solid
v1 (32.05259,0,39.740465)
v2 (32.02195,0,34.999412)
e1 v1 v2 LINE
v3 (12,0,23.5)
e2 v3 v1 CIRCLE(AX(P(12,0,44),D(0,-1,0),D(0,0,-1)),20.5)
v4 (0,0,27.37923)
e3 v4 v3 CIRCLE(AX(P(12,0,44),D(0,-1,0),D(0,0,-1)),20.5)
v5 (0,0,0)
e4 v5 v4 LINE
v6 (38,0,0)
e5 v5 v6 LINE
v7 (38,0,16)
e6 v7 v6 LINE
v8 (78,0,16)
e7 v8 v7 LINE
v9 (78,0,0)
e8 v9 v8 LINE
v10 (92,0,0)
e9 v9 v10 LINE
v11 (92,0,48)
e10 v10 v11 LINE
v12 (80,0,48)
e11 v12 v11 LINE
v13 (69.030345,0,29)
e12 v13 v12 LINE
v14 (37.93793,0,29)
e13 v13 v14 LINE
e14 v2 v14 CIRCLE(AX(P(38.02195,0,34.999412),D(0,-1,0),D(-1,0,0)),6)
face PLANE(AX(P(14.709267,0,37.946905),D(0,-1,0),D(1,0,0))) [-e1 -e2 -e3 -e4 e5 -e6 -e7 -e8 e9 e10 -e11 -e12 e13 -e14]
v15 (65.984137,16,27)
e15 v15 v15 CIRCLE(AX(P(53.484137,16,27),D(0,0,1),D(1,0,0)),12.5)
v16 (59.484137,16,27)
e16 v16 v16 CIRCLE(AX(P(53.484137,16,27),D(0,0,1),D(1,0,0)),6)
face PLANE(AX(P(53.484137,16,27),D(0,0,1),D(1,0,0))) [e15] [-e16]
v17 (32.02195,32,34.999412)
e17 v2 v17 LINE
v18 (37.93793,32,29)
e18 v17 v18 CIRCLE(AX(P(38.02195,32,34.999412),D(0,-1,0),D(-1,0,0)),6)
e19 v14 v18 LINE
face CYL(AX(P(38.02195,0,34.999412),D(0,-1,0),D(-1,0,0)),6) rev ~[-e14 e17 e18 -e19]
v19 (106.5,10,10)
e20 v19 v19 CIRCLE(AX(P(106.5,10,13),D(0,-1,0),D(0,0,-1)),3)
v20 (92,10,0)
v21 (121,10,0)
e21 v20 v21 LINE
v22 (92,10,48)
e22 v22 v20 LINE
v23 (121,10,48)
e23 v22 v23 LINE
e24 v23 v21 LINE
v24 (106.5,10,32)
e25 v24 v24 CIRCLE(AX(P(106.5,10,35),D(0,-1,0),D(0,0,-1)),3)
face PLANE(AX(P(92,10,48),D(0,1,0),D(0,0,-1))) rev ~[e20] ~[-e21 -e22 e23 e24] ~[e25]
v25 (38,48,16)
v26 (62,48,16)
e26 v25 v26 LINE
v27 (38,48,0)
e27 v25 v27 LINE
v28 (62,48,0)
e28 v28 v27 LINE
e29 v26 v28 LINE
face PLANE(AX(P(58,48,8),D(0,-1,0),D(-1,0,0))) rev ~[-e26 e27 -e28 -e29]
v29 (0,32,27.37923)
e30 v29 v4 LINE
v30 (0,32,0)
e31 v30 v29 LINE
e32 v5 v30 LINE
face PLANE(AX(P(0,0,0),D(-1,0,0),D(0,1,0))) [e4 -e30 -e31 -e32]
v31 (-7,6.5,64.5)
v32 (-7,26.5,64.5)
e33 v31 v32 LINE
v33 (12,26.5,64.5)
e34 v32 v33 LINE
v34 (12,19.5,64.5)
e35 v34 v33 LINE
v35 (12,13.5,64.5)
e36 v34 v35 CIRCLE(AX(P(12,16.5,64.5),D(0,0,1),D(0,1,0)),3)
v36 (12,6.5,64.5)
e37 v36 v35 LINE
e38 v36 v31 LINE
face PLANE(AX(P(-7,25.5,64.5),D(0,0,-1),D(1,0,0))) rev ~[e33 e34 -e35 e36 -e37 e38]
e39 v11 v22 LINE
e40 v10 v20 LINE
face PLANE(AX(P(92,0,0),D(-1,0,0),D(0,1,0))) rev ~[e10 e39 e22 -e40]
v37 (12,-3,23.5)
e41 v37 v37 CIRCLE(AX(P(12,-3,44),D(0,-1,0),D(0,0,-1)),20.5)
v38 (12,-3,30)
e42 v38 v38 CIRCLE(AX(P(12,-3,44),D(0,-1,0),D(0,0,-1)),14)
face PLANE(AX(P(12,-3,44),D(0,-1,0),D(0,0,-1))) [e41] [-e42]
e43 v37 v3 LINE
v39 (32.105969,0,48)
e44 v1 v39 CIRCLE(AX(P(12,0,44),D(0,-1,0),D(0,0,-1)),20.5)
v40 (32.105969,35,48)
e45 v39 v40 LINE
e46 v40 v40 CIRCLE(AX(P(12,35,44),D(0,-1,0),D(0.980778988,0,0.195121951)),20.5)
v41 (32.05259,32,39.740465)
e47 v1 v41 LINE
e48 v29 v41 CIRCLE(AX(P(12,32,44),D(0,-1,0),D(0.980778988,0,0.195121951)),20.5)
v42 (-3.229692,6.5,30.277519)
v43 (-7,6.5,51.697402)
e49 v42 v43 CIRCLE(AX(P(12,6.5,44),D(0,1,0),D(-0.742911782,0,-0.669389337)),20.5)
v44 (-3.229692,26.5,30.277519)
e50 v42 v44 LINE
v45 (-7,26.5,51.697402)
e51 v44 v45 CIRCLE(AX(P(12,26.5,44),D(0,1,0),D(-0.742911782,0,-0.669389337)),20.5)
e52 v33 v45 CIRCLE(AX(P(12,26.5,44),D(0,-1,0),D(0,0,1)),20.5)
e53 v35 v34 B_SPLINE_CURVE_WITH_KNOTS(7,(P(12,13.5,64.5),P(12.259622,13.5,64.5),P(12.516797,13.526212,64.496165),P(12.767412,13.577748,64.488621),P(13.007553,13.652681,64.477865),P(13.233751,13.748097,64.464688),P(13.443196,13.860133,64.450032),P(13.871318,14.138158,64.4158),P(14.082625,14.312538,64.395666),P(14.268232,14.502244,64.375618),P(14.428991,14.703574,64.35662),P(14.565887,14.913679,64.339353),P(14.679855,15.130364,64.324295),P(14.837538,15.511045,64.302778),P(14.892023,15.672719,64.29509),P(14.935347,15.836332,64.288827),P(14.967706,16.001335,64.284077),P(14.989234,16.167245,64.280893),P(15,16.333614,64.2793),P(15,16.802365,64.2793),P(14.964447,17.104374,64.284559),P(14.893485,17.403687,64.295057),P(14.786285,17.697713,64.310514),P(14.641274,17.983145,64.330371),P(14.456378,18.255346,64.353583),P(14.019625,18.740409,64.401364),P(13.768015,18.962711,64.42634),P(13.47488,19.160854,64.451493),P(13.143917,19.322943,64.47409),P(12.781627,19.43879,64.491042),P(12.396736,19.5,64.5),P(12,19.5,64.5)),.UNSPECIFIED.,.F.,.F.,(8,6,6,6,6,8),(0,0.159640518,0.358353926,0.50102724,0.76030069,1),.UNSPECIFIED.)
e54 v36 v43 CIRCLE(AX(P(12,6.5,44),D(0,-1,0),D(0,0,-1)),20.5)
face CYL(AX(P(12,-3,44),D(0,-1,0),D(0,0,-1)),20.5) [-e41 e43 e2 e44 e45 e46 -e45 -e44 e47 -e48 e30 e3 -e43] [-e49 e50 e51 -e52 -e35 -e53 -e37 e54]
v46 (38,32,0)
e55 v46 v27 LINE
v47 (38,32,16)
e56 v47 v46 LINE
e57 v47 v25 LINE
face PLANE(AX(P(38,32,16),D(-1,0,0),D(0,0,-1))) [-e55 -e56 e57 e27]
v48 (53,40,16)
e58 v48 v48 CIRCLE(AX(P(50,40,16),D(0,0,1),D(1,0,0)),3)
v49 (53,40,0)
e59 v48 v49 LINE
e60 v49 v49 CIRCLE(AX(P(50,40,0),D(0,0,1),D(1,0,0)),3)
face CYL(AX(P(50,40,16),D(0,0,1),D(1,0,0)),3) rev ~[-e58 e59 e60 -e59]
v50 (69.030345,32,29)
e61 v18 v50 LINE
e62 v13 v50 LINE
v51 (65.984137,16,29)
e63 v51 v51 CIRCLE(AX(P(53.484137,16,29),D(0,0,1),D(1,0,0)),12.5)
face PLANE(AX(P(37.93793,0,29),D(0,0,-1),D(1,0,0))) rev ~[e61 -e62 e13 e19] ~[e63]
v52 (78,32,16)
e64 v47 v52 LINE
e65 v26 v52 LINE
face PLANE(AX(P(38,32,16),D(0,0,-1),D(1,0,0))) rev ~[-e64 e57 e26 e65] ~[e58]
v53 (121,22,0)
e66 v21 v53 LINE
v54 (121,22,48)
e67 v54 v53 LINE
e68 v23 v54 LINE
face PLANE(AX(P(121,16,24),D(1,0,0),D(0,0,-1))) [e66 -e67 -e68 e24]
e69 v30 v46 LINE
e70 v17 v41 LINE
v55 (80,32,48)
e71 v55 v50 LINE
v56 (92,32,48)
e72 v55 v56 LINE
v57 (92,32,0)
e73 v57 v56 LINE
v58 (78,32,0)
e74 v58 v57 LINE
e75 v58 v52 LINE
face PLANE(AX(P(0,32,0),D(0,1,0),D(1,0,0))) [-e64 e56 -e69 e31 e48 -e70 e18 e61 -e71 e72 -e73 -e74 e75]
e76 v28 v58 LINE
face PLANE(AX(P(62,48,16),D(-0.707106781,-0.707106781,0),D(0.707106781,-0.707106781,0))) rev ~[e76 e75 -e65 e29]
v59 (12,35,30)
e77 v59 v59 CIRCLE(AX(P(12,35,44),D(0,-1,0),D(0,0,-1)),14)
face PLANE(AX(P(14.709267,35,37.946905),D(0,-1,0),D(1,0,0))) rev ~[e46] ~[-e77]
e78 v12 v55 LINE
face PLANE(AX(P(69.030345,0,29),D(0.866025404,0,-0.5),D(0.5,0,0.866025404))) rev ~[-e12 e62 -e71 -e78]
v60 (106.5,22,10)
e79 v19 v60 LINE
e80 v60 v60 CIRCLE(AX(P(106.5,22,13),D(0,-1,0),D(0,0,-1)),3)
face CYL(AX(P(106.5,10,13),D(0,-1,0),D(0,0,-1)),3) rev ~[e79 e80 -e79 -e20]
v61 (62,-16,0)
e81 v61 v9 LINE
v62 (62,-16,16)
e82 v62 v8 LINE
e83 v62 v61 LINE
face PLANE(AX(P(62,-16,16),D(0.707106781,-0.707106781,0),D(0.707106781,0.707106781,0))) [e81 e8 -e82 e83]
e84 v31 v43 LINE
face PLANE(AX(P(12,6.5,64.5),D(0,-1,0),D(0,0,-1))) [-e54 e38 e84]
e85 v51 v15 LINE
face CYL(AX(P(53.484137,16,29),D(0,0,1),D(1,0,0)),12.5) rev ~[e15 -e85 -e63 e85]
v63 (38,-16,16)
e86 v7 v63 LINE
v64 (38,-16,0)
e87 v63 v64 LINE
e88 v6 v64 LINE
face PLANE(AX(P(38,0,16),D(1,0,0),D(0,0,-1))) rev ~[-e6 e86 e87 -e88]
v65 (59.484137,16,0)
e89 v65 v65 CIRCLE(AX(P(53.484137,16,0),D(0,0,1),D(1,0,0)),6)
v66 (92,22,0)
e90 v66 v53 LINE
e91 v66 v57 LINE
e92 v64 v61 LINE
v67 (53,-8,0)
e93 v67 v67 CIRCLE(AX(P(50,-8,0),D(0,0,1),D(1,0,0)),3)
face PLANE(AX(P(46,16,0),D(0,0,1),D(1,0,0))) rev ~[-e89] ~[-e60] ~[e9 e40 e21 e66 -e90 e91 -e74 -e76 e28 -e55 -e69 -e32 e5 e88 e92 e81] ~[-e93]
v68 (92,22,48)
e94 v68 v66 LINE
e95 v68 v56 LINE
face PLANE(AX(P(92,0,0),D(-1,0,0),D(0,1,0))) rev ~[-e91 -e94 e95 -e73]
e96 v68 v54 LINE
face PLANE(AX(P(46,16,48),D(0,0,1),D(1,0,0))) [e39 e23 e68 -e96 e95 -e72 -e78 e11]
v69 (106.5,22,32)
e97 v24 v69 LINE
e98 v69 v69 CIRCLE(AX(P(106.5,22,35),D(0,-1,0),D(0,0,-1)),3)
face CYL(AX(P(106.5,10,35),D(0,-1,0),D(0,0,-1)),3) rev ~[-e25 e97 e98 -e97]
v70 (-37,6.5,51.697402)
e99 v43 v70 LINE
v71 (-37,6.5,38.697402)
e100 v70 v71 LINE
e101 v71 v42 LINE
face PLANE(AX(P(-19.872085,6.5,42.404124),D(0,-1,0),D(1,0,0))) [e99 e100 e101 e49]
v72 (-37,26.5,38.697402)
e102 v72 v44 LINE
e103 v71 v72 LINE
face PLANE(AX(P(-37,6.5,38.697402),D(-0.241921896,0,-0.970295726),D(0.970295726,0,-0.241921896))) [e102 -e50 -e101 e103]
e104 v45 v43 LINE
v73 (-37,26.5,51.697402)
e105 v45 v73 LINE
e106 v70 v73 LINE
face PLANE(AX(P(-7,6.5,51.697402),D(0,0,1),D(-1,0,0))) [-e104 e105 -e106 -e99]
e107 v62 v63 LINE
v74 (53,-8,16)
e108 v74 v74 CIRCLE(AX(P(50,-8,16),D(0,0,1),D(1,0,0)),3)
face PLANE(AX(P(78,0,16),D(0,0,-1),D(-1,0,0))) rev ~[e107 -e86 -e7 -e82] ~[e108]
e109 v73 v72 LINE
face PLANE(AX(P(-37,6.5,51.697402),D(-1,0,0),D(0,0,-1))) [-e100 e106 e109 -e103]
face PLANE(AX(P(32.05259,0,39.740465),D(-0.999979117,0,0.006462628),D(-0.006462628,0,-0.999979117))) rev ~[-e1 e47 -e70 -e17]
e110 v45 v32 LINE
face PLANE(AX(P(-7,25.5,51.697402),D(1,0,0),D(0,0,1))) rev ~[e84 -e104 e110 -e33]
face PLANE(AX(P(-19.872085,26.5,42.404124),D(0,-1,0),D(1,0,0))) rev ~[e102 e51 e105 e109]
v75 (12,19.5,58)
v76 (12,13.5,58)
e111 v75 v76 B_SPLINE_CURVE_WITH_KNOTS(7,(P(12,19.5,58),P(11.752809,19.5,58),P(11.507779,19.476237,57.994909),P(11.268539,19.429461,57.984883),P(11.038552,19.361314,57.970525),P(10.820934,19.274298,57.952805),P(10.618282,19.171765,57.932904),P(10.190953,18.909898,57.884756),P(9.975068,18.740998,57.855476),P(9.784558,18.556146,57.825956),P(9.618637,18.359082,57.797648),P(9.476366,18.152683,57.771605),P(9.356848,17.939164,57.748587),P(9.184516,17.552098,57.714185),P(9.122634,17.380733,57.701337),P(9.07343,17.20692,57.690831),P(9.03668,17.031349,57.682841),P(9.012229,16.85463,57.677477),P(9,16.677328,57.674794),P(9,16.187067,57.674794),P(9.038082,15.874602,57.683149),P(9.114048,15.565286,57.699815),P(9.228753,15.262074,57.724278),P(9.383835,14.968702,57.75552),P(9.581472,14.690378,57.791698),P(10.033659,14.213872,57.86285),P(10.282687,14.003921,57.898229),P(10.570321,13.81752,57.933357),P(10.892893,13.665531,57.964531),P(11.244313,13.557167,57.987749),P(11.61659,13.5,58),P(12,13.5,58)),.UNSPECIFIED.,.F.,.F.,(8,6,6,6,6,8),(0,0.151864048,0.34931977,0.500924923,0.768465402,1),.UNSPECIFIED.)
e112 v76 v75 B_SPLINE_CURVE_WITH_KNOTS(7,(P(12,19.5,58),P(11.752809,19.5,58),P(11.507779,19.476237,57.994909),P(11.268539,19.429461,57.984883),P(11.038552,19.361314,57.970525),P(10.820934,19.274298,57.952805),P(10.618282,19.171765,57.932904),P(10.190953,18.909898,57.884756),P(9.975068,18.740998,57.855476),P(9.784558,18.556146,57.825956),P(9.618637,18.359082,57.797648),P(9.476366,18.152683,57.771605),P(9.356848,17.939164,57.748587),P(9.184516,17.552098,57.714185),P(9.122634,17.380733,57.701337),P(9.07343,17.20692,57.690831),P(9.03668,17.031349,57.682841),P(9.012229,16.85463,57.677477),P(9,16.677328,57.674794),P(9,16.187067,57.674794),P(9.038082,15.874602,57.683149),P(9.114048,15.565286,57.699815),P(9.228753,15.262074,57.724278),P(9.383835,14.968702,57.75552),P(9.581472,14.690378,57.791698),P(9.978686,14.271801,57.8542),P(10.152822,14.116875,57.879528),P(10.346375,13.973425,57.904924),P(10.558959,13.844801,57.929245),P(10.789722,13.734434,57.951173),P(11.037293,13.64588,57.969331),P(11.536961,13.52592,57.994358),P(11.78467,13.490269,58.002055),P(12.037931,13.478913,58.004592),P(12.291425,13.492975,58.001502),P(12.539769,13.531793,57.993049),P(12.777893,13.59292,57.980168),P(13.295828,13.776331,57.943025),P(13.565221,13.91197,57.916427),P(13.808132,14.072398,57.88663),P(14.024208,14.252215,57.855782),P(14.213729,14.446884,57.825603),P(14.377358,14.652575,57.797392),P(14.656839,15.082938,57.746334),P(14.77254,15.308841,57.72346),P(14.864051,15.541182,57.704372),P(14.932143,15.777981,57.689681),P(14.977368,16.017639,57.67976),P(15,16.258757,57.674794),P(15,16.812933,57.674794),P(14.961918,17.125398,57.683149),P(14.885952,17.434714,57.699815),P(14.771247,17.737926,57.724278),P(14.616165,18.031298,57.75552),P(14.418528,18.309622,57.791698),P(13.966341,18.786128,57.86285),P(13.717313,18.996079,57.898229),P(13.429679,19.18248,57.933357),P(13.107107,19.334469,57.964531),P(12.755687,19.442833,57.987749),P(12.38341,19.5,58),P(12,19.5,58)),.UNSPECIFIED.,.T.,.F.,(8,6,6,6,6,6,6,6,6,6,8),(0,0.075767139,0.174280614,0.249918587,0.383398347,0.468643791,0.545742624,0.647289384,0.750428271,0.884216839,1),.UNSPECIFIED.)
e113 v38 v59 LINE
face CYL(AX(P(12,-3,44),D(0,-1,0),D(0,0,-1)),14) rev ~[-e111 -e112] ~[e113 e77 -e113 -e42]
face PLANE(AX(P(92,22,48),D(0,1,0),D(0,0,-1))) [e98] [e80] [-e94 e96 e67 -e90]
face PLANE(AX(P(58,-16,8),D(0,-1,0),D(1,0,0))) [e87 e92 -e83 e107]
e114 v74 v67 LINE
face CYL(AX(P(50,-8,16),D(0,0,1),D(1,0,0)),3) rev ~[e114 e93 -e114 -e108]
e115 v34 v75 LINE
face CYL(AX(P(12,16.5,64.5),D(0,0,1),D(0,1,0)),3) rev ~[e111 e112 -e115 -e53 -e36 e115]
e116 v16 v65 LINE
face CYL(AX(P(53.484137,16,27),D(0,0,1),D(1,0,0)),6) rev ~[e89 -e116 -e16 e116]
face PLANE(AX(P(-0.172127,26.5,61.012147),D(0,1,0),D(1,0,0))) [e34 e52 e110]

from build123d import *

# Parameters (mm, degrees)
BASE_BLOCK_SKETCH_W           = 92
BASE_BLOCK_SKETCH_H           = 32
BASE_BLOCK_DEPTH              = 48
MOUNTING_FLANGE_SKETCH_W      = 48
MOUNTING_FLANGE_SKETCH_H      = 12.000000000000002
MOUNTING_FLANGE_DEPTH         = 29
FLANGE_HOLES_SKETCH_R         = 2.999999999999994
FLANGE_HOLES_SKETCH_R_2       = 2.9999999999999947
FLANGE_HOLES_2X_DEPTH         = 29
UPRIGHT_LUG_DEPTH             = 16
UPRIGHT_LUG_CHAMFER_CUT_DEPTH = 16
SIDE_LUG_DEPTH                = 16
SIDE_LUG_CHAMFER_CUT_DEPTH    = 16
UPRIGHT_LUG_HOLE_SKETCH_R     = 3.0000000000000018
UPRIGHT_LUG_HOLE_SKETCH_R_2   = 3.000000000000001
UPRIGHT_LUG_HOLE_DEPTH        = 16
HUB_BODY_DEPTH                = 35
HUB_START                     = 3
HUB_COLLAR_SKETCH_R           = 20.5
HUB_COLLAR_41_DEPTH           = 3
HUB_BORE_SKETCH_R             = 13.999999999999996
HUB_BORE_28_DEPTH             = 38
ANGLED_RELIEF_CUT_30DEG_DEPTH = 38
RELIEF_POCKET_DEPTH           = 38
SPOT_FACE_SKETCH_R            = 12.500000000000002
SPOT_FACE_RECESS_DEPTH        = 2
THROUGH_HOLE_SKETCH_R         = 6.000000000000003
THROUGH_HOLE_12_DEPTH         = 30
ARM_BLOCK_SKETCH_W            = 12.999999999999993
ARM_BLOCK_SKETCH_H            = 19.000000000000004
ARM_BLOCK_DEPTH               = 19
CLAMP_LUG_DEPTH               = 20
CLAMP_PAD_DEPTH               = 1
CLAMP_HOLE_SKETCH_R           = 3.0000000000000004
CLAMP_HOLE_6_DEPTH            = 20
HUB_SLOT_CUT_DEPTH            = 20


with BuildPart() as part:
    # Base Block Sketch → Base Block (new body)
    with BuildSketch(Plane.XY):
        with Locations((46, 16)):
            Rectangle(BASE_BLOCK_SKETCH_W, BASE_BLOCK_SKETCH_H)
    extrude(amount=BASE_BLOCK_DEPTH)

    # Mounting Flange Sketch → Mounting Flange (add)
    with BuildSketch(Plane(origin=(92, 0, 0), x_dir=(0, 0, -1), z_dir=(1, 0, 0))):
        with Locations((-24, 16)):
            Rectangle(MOUNTING_FLANGE_SKETCH_W, MOUNTING_FLANGE_SKETCH_H)
    extrude(amount=MOUNTING_FLANGE_DEPTH)

    # Flange Holes Sketch → Flange Holes 2x (cut)
    with BuildSketch(Plane.XZ.offset(-9.999999999999998)):
        with Locations(Location((106.5, 13, 0), (0, 0, 270))):
            Circle(FLANGE_HOLES_SKETCH_R)
        with Locations(Location((106.5, 34.99999999999999, 0), (0, 0, 270))):
            Circle(FLANGE_HOLES_SKETCH_R_2)
    extrude(amount=-FLANGE_HOLES_2X_DEPTH, mode=Mode.SUBTRACT)

    # Upright Lug Sketch → Upright Lug (add)
    with BuildSketch(Plane.XZ):
        Polygon((38, 0), (62, 0), (78, 0), (78, 16), (62, 16), (38, 16), align=None)
    extrude(amount=UPRIGHT_LUG_DEPTH)

    # Upright Lug Chamfer Sketch → Upright Lug Chamfer Cut (cut)
    with BuildSketch(Plane.XY.offset(16)):
        Polygon((78, -16), (62, -16), (78, 0), align=None)
    extrude(amount=-UPRIGHT_LUG_CHAMFER_CUT_DEPTH, mode=Mode.SUBTRACT)

    # Side Lug Sketch → Side Lug (add)
    with BuildSketch(Plane(origin=(0, 32, 0), x_dir=(1, 0, 0), z_dir=(0, 1, 0))):
        Polygon((38, 0), (62, 0), (78, 0), (78, -16), (62, -16), (38, -16), align=None)
    extrude(amount=SIDE_LUG_DEPTH)

    # Side Lug Chamfer Sketch → Side Lug Chamfer Cut (cut)
    with BuildSketch(Plane.XY.offset(16)):
        Polygon((78, 48), (62, 48), (78, 32), align=None)
    extrude(amount=-SIDE_LUG_CHAMFER_CUT_DEPTH, mode=Mode.SUBTRACT)

    # Upright Lug Hole Sketch → Upright Lug Hole (cut)
    with BuildSketch(Plane.XY.offset(16)):
        with Locations((50, 40)):
            Circle(UPRIGHT_LUG_HOLE_SKETCH_R)
        with Locations((50, -8)):
            Circle(UPRIGHT_LUG_HOLE_SKETCH_R_2)
    extrude(amount=-UPRIGHT_LUG_HOLE_DEPTH, mode=Mode.SUBTRACT)

    # Hub Body Sketch → Hub Body (add)
    with BuildSketch(Plane.XZ):
        with BuildLine():
            ThreePointArc((3.3573e-13, 27.379229861405094), (21.334077351297417, 25.748287751556113), (32.5, 43.99999999999999))
            ThreePointArc((32.5, 44), (32.4012544943822, 46.009680336633146), (32.10596926288294, 48.00000000000083))
            Line((32.10596926288278, 48), (0, 48))
            Line((0, 48), (0, 27.379229861404976))
        make_face()
        with BuildLine():
            Line((0, 48), (32.10596926288278, 48))
            ThreePointArc((32.10596926288294, 48.00000000000083), (0.9216100131877187, 61.24874706464494), (3.3573e-13, 27.379229861405094))
            Line((0, 27.379229861404976), (0, 48))
        make_face()
    extrude(amount=-HUB_BODY_DEPTH)

    # Hub Collar Sketch → Hub Collar Ø41 (add)
    with BuildSketch(Plane.XZ.offset(HUB_START)):
        with Locations(Location((11.999999999999998, 44, 0), (0, 0, 270))):
            Circle(HUB_COLLAR_SKETCH_R)
    extrude(amount=-HUB_COLLAR_41_DEPTH)

    # Hub Bore Sketch → Hub Bore Ø28 (cut)
    with BuildSketch(Plane.XZ.offset(3)):
        with Locations(Location((11.999999999999998, 44, 0), (0, 0, 270))):
            Circle(HUB_BORE_SKETCH_R)
    extrude(amount=-HUB_BORE_28_DEPTH, mode=Mode.SUBTRACT)

    # Angled Relief Sketch → Angled Relief Cut 30deg (cut)
    with BuildSketch(Plane.XZ):
        Polygon((69.03034488539707, 29.00000000000001), (79.99999999999999, 48), (38.10596926288314, 48), (38.1059692628831, 29), (67.89066123526882, 29), align=None)
    extrude(amount=-ANGLED_RELIEF_CUT_30DEG_DEPTH, mode=Mode.SUBTRACT)

    # Relief Pocket Sketch → Relief Pocket (cut)
    with BuildSketch(Plane.XZ):
        with BuildLine():
            Line((32.052589846453245, 39.74046476127714), (32.021949545440904, 34.99941169508152))
            ThreePointArc((32.021949545440904, 34.99941169508152), (33.74970667402833, 30.786581192003514), (37.93792982799573, 29.00000000000004))
            Line((37.93792982799573, 29), (38.1059692628831, 29))
            Line((38.1059692628831, 29), (38.10596926288314, 48))
            Line((38.10596926288314, 48), (32.1059692628831, 48))
            ThreePointArc((32.10596926288309, 48), (32.499571898565115, 43.8675161309467), (32.0525898464532, 39.74046476127714))
        make_face()
    extrude(amount=-RELIEF_POCKET_DEPTH, mode=Mode.SUBTRACT)

    # Spot Face Sketch → Spot Face Recess (cut)
    with BuildSketch(Plane.XY.offset(29)):
        with Locations((53.48413735669789, 16)):
            Circle(SPOT_FACE_SKETCH_R)
    extrude(amount=-SPOT_FACE_RECESS_DEPTH, mode=Mode.SUBTRACT)

    # Through Hole Sketch → Through Hole Ø12 (cut)
    with BuildSketch(Plane.XY.offset(27.000000000000004)):
        with Locations((53.48413735669789, 16)):
            Circle(THROUGH_HOLE_SKETCH_R)
    extrude(amount=-THROUGH_HOLE_12_DEPTH, mode=Mode.SUBTRACT)

    # Arm Block Sketch → Arm Block (add)
    with BuildSketch(Plane(origin=(12, 0, 0), x_dir=(0, 0, -1), z_dir=(1, 0, 0))):
        with Locations((-58, 16)):
            Rectangle(ARM_BLOCK_SKETCH_W, ARM_BLOCK_SKETCH_H)
    extrude(amount=-ARM_BLOCK_DEPTH)

    # Clamp Lug Sketch → Clamp Lug (add)
    with BuildSketch(Plane.XZ.offset(-6.499999999999999)):
        with BuildLine():
            Line((-6.999999999999999, 51.69740215917034), (-37, 51.69740215917034))
            Line((-37, 51.69740215917034), (-37, 38.697402159170345))
            Line((-37, 38.697402159170345), (-3.229691527211141, 30.277518592251866))
            ThreePointArc((-3.229691527211141, 30.277518592251866), (-8.189621059274332, 40.446241217681404), (-6.999999999999999, 51.69740215917034))
        make_face()
    extrude(amount=-CLAMP_LUG_DEPTH)

    # Clamp Pad Sketch → Clamp Pad (add)
    with BuildSketch(Plane(origin=(0, 25.5, 0), x_dir=(1, 0, 0), z_dir=(0, 1, 0))):
        with BuildLine():
            Line((-6.999999999999999, -51.69740215917034), (-6.999999999999999, -64.5))
            Line((-6.999999999999999, -64.5), (11.999999999999998, -64.5))
            ThreePointArc((11.999999999999998, -64.5), (0.5445808514701636, -61.00068740173455), (-6.999999999999999, -51.69740215917034))
        make_face()
    extrude(amount=CLAMP_PAD_DEPTH)

    # Clamp Hole Sketch → Clamp Hole Ø6 (cut)
    with BuildSketch(Plane.XY.offset(64.5)):
        with Locations(Location((12, 16.5, 0), (0, 0, 90))):
            Circle(CLAMP_HOLE_SKETCH_R)
    extrude(amount=-CLAMP_HOLE_6_DEPTH, mode=Mode.SUBTRACT)

    # Hub Slot Sketch → Hub Slot Cut (cut)
    with BuildSketch(Plane.XZ.offset(-6.499999999999999)):
        with BuildLine():
            Line((12, 51.50000000000001), (12, 57.99999999999999))
            ThreePointArc((12, 57.99999999999999), (5.254631218383986, 56.26784414638529), (0.17840958246311683, 51.50000000000001))
            Line((0.17840958246311683, 51.50000000000001), (12, 51.50000000000001))
        make_face()
    extrude(amount=-HUB_SLOT_CUT_DEPTH, mode=Mode.SUBTRACT)


solid = part.part
